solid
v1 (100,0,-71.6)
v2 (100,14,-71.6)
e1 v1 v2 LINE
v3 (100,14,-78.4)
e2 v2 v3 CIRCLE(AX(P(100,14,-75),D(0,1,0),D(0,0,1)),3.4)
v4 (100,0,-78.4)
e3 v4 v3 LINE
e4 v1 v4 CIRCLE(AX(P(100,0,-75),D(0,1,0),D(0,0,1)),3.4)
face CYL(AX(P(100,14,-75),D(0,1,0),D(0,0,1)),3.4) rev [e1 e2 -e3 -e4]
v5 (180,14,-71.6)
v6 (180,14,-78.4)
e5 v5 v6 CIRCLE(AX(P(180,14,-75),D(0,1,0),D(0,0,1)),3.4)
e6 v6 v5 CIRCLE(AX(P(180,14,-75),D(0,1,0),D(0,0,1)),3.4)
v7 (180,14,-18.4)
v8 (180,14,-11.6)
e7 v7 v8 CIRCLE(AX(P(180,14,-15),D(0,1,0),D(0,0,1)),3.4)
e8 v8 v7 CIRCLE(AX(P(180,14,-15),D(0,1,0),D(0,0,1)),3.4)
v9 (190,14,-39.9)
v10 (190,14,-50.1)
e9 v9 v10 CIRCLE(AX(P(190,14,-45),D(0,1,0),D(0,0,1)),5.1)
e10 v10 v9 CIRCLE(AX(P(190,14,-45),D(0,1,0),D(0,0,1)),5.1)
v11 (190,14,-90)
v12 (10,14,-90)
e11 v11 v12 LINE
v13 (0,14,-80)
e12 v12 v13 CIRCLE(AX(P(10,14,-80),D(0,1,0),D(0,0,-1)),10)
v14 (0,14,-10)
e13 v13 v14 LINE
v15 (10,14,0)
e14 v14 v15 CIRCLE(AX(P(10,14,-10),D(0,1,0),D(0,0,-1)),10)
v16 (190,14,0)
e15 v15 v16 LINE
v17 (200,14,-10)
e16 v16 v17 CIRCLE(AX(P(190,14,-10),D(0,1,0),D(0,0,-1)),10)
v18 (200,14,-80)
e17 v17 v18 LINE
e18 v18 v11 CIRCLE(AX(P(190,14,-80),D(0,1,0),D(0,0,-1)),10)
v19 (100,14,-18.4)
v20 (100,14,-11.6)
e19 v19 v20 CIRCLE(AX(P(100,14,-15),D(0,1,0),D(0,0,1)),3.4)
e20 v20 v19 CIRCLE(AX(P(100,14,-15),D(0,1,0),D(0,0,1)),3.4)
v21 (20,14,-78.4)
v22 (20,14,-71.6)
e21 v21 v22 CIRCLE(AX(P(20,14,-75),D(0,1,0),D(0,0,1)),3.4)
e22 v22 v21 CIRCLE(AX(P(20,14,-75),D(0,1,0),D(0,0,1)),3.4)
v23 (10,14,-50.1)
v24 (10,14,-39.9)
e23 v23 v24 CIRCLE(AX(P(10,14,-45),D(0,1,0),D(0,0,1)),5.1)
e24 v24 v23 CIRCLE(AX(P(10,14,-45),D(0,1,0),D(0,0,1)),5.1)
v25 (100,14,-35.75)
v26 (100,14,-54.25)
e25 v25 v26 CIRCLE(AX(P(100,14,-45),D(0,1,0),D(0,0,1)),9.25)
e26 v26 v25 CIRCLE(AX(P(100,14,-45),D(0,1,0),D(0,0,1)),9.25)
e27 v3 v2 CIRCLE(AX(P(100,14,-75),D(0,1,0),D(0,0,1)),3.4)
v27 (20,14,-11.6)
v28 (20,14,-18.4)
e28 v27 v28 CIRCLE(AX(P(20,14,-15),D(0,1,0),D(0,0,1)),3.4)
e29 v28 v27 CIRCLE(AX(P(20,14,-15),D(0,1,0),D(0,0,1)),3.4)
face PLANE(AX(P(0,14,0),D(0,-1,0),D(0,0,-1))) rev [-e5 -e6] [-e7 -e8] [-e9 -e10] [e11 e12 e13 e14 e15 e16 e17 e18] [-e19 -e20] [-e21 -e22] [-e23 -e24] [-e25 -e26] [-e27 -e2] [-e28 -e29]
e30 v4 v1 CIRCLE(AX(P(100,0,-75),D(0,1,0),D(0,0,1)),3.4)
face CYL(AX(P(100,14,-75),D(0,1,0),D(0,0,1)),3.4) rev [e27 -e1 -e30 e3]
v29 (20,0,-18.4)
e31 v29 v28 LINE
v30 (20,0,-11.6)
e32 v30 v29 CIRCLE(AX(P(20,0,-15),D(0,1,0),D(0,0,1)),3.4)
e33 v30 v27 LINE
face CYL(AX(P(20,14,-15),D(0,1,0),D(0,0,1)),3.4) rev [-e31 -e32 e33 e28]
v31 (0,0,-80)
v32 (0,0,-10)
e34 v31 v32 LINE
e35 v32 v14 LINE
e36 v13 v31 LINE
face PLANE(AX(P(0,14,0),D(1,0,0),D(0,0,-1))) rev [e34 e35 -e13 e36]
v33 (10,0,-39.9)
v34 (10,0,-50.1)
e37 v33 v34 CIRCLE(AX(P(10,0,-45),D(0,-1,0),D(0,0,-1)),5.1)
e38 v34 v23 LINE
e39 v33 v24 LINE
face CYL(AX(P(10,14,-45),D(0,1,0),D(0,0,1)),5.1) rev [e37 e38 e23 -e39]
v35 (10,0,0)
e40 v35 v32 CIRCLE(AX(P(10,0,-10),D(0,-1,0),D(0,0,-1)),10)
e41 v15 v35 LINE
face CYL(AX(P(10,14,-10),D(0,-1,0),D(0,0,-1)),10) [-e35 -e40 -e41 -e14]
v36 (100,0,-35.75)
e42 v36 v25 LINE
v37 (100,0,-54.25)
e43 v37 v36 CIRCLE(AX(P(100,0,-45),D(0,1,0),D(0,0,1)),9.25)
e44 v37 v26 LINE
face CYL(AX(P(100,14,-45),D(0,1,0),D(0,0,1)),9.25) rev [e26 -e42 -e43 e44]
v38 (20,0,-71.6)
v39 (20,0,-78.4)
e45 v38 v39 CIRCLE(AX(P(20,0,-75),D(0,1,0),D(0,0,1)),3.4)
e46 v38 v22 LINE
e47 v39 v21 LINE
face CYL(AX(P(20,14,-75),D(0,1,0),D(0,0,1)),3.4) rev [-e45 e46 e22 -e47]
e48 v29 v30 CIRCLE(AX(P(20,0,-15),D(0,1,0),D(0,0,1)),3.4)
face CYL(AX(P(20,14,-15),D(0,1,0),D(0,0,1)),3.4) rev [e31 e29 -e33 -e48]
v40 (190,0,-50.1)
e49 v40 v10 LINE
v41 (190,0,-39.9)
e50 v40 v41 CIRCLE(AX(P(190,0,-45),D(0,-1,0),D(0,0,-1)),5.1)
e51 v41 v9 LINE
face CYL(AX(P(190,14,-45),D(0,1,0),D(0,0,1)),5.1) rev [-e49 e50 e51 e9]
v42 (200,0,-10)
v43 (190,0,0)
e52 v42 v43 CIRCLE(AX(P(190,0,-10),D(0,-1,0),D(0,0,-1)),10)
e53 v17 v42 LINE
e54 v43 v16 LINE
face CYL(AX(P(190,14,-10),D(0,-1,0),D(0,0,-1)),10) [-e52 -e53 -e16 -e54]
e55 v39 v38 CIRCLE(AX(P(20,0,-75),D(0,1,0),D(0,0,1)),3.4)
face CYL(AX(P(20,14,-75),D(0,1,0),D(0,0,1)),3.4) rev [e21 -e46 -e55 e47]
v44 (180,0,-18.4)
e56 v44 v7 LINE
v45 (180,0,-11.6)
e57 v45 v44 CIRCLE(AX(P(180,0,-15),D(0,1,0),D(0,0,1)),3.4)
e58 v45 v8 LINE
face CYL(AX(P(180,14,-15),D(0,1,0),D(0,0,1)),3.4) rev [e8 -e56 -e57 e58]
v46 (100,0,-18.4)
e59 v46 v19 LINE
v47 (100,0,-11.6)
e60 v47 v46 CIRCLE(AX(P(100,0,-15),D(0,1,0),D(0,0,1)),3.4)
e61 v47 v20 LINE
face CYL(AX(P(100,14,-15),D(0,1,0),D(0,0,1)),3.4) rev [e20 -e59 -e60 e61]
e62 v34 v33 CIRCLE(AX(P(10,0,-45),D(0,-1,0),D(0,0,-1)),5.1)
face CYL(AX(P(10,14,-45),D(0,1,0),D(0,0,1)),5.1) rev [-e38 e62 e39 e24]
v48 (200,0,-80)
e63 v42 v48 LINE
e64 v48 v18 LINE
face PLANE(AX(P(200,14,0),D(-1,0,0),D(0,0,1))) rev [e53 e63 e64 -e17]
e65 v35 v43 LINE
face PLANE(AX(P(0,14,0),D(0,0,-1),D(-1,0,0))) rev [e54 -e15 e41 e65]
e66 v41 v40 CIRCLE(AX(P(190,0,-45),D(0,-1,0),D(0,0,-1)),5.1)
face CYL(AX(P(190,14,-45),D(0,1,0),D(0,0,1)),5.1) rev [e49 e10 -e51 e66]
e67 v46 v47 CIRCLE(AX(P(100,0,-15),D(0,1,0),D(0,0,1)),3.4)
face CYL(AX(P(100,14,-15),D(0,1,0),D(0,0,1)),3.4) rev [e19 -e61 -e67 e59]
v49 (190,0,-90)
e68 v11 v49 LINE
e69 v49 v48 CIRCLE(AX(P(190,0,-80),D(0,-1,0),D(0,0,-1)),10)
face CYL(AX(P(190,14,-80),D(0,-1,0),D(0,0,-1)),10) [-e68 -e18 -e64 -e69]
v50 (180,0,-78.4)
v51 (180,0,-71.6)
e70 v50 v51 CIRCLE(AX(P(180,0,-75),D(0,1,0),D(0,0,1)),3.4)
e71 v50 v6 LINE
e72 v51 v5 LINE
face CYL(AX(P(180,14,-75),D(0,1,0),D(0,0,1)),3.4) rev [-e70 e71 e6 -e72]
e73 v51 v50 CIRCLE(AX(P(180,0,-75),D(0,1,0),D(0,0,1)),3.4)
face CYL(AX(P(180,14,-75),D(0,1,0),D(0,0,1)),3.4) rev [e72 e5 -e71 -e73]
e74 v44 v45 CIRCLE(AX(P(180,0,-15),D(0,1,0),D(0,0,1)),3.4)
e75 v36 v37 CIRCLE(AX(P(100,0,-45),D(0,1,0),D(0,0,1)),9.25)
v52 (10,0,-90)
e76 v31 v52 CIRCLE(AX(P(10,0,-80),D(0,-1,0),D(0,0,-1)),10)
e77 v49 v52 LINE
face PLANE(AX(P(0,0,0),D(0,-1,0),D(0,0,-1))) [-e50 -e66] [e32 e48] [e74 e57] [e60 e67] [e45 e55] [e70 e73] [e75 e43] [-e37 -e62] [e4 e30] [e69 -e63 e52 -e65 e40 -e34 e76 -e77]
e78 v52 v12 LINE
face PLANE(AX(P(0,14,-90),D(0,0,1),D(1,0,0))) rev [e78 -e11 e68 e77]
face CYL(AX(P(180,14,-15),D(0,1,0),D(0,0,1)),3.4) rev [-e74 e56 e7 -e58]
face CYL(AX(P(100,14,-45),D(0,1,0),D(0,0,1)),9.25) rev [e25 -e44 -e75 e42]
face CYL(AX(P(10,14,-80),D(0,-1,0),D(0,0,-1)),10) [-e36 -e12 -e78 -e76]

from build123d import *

# Parameters (mm, degrees)
SKETCH1_W              = 200
SKETCH1_H              = 90
BOSS_EXTRUDE1_DEPTH    = 14
M12_TAPPED_HOLE1_D     = 10.2
M12_TAPPED_HOLE1_DEPTH = 29.25
M12_TAPPED_HOLE1_TIP   = 3.064389157
FILLET1_R              = 10
M20X1_5_TAPPED_HOLE1_D = 18.5
M8_TAPPED_HOLE1_D      = 6.8


with BuildPart() as part:
    # Sketch1 → Boss-Extrude1 (new body)
    with BuildSketch(Plane(origin=(0, 0, 0), x_dir=(1, 0, 0), z_dir=(0, 1, 0))):
        with Locations((100, 45)):
            Rectangle(SKETCH1_W, SKETCH1_H)
    extrude(amount=BOSS_EXTRUDE1_DEPTH)

    # M12 Tapped Hole1
    with Locations(Plane(origin=(0, 14, 0), x_dir=(1, 0, 0), z_dir=(0, 1, 0))):
        with Locations((10, 45), (190, 45)):
            Hole(M12_TAPPED_HOLE1_D / 2, depth=M12_TAPPED_HOLE1_DEPTH)
            with Locations((0, 0, -(M12_TAPPED_HOLE1_DEPTH + M12_TAPPED_HOLE1_TIP / 2))):  # 118° drill point
                Cone(0, M12_TAPPED_HOLE1_D / 2, M12_TAPPED_HOLE1_TIP, mode=Mode.SUBTRACT)

    # Fillet1
    fillet1_edges = [part.edges().sort_by_distance(p)[0] for p in [
        (0, 7, -90),
        (200, 7, -90),
        (200, 7, 0),
        (0, 7, 0),
    ]]
    fillet(fillet1_edges, radius=FILLET1_R)

    # M20x1.5 Tapped Hole1 (through all)
    with Locations(Plane(origin=(0, 14, 0), x_dir=(1, 0, 0), z_dir=(0, 1, 0))):
        with Locations((100, 45)):
            Hole(M20X1_5_TAPPED_HOLE1_D / 2)

    # M8 Tapped Hole1 (through all)
    with Locations(Plane(origin=(0, 14, 0), x_dir=(1, 0, 0), z_dir=(0, 1, 0))):
        with Locations((20, 75), (100, 75), (180, 75), (180, 15), (100, 15), (20, 15)):
            Hole(M8_TAPPED_HOLE1_D / 2)


solid = part.part
